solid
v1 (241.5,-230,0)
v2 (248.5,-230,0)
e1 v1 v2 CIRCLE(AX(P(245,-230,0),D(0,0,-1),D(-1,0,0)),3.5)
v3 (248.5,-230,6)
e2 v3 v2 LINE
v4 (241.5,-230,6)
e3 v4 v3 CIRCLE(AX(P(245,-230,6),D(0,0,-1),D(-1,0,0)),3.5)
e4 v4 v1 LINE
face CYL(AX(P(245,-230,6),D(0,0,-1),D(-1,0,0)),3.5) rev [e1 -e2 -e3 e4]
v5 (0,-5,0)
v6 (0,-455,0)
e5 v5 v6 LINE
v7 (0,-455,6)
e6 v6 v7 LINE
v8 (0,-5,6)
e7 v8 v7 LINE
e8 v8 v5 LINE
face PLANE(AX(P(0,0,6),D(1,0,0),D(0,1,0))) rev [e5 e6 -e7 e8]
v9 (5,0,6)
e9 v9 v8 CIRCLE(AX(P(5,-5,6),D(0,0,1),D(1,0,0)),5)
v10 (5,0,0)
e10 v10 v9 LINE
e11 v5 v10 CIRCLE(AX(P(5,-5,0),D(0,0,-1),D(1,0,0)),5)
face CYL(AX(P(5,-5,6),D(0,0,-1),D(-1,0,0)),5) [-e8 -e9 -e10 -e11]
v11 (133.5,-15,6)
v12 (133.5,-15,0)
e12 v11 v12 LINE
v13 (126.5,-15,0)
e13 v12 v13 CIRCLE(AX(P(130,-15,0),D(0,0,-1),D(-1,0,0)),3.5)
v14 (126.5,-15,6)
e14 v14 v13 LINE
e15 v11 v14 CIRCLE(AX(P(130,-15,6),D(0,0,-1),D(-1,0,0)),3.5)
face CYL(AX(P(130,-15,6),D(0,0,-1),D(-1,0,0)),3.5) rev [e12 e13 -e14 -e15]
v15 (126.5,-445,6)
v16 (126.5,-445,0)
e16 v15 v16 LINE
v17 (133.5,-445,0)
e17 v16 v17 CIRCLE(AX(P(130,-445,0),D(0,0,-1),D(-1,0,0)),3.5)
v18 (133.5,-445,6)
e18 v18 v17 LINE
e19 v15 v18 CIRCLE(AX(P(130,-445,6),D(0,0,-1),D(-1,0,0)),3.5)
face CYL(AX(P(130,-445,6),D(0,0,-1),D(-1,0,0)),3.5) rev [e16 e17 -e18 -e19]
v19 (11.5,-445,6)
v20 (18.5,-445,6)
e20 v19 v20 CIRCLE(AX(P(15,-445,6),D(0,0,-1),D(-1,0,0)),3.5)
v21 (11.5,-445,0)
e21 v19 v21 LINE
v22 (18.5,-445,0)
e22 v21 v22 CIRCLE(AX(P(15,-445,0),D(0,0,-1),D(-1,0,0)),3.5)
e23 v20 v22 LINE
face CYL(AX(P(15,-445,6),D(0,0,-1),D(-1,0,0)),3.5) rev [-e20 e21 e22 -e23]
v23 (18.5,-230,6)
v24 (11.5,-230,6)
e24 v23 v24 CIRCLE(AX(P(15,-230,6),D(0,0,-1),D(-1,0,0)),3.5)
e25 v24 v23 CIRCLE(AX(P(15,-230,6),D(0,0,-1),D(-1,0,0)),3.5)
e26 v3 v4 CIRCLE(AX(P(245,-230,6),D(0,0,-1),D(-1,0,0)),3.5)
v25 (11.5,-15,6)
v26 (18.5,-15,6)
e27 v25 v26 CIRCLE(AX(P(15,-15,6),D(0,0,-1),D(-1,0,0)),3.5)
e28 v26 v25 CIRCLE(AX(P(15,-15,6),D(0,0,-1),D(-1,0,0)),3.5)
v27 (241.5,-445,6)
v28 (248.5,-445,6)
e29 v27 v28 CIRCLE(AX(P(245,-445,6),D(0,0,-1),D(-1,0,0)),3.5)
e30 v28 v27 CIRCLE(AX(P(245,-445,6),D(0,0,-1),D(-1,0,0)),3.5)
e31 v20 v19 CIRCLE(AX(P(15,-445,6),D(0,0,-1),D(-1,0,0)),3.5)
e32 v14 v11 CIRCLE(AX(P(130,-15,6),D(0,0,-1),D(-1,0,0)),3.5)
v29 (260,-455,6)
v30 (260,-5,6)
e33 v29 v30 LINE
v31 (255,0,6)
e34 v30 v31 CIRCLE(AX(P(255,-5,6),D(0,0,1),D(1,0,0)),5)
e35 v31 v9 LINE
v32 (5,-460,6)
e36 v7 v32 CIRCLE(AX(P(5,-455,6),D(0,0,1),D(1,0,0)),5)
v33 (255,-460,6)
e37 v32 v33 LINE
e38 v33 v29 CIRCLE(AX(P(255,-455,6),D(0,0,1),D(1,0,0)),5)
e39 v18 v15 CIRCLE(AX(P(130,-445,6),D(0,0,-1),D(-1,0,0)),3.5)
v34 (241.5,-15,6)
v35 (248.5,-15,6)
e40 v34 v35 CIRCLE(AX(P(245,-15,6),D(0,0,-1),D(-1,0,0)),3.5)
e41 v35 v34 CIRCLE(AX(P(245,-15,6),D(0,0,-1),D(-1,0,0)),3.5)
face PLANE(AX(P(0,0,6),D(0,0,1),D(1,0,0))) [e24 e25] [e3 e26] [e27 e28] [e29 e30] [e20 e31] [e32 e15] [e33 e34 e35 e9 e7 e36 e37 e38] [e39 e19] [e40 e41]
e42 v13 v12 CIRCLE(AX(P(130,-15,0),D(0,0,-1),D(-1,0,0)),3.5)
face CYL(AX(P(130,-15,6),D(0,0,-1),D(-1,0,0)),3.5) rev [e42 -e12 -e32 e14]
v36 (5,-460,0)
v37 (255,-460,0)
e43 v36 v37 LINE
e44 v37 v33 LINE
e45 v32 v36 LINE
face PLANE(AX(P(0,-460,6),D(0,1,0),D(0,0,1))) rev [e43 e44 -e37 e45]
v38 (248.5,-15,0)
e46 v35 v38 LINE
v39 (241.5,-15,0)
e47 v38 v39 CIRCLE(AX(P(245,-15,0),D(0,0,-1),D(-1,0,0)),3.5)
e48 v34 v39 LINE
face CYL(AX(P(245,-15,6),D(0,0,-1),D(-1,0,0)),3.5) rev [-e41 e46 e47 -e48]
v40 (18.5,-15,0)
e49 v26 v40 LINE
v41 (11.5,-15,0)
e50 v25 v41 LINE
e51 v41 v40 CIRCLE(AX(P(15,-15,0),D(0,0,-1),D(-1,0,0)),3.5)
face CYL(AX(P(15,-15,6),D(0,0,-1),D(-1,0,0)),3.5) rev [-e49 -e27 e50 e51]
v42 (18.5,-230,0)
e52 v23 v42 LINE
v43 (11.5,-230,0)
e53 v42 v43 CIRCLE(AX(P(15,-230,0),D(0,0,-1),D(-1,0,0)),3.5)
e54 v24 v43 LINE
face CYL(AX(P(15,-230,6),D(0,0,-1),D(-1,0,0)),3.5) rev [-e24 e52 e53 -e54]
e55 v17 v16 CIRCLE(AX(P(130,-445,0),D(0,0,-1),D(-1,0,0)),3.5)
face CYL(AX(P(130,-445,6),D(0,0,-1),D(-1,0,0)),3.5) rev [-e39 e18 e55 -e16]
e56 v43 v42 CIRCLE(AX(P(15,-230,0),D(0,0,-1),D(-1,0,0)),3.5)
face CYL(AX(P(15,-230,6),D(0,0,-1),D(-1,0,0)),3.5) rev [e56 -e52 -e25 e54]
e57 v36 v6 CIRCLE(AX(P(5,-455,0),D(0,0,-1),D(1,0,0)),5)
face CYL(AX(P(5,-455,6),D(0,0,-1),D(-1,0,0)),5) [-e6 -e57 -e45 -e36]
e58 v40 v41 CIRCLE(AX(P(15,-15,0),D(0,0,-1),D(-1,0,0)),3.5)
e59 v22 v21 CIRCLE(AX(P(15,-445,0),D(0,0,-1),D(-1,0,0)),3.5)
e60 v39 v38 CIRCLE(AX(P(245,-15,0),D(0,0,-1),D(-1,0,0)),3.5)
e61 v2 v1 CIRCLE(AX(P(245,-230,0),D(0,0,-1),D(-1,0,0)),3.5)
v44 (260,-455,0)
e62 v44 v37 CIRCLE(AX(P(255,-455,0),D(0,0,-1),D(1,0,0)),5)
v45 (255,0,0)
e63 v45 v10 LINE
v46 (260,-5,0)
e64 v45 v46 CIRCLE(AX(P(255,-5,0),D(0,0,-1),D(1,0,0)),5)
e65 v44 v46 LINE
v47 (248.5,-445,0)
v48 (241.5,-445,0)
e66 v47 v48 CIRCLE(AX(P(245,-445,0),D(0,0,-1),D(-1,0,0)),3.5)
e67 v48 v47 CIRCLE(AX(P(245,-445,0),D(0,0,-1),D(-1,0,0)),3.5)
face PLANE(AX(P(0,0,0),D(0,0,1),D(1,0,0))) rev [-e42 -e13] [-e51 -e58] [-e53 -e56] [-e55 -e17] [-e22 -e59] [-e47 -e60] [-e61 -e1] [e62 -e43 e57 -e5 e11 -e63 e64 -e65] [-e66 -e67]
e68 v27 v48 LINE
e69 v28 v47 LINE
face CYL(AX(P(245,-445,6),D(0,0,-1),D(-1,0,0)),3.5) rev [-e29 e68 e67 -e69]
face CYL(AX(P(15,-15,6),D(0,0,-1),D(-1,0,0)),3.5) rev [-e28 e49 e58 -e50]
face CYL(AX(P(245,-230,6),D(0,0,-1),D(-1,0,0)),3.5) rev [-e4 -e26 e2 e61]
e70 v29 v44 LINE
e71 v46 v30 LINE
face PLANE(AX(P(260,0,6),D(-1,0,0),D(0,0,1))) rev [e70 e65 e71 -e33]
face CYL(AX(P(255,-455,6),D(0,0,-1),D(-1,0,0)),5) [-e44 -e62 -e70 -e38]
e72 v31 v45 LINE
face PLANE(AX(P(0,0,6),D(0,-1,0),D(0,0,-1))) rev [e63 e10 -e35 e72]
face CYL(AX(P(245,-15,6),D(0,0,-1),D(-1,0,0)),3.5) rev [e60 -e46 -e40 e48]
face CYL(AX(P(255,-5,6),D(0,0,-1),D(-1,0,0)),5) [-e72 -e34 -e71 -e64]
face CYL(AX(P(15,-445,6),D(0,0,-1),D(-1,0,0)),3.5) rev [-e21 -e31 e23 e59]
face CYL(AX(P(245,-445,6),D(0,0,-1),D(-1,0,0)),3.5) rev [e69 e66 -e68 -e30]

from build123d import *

# Parameters (mm, degrees)
SKETCH_1_W          = 260
SKETCH_1_H          = 460
EXTRUDE_1_DEPTH     = 6
FILLET_1_R          = 5
SKETCH_2_R          = 3.5
CUT_EXTRUDE_1_DEPTH = 529.427856949


with BuildPart() as part:
    # 草图1 → 凸台-拉伸1 (new body)
    with BuildSketch(Plane.XY):
        with Locations((130, -230)):
            Rectangle(SKETCH_1_W, SKETCH_1_H)
    extrude(amount=EXTRUDE_1_DEPTH)

    # 圆角1
    fillet_1_edges = [part.edges().sort_by_distance(p)[0] for p in [
        (0, 0, 3),
        (260, 0, 3),
        (260, -460, 3),
        (0, -460, 3),
    ]]
    fillet(fillet_1_edges, radius=FILLET_1_R)

    # 草图2 → 切除-拉伸1 (cut, through all)
    with BuildSketch(Plane(origin=(0, 0, 0), x_dir=(-1, 0, 0), z_dir=(0, 0, -1))):
        with Locations((-245, -445)):
            Circle(SKETCH_2_R)
        with Locations((-15, -445)):
            Circle(SKETCH_2_R)
        with Locations((-245, -15)):
            Circle(SKETCH_2_R)
        with Locations((-15, -15)):
            Circle(SKETCH_2_R)
        with Locations((-130, -445)):
            Circle(SKETCH_2_R)
        with Locations((-245, -230)):
            Circle(SKETCH_2_R)
        with Locations((-130, -15)):
            Circle(SKETCH_2_R)
        with Locations((-15, -230)):
            Circle(SKETCH_2_R)
    extrude(amount=-CUT_EXTRUDE_1_DEPTH, mode=Mode.SUBTRACT)


solid = part.part
